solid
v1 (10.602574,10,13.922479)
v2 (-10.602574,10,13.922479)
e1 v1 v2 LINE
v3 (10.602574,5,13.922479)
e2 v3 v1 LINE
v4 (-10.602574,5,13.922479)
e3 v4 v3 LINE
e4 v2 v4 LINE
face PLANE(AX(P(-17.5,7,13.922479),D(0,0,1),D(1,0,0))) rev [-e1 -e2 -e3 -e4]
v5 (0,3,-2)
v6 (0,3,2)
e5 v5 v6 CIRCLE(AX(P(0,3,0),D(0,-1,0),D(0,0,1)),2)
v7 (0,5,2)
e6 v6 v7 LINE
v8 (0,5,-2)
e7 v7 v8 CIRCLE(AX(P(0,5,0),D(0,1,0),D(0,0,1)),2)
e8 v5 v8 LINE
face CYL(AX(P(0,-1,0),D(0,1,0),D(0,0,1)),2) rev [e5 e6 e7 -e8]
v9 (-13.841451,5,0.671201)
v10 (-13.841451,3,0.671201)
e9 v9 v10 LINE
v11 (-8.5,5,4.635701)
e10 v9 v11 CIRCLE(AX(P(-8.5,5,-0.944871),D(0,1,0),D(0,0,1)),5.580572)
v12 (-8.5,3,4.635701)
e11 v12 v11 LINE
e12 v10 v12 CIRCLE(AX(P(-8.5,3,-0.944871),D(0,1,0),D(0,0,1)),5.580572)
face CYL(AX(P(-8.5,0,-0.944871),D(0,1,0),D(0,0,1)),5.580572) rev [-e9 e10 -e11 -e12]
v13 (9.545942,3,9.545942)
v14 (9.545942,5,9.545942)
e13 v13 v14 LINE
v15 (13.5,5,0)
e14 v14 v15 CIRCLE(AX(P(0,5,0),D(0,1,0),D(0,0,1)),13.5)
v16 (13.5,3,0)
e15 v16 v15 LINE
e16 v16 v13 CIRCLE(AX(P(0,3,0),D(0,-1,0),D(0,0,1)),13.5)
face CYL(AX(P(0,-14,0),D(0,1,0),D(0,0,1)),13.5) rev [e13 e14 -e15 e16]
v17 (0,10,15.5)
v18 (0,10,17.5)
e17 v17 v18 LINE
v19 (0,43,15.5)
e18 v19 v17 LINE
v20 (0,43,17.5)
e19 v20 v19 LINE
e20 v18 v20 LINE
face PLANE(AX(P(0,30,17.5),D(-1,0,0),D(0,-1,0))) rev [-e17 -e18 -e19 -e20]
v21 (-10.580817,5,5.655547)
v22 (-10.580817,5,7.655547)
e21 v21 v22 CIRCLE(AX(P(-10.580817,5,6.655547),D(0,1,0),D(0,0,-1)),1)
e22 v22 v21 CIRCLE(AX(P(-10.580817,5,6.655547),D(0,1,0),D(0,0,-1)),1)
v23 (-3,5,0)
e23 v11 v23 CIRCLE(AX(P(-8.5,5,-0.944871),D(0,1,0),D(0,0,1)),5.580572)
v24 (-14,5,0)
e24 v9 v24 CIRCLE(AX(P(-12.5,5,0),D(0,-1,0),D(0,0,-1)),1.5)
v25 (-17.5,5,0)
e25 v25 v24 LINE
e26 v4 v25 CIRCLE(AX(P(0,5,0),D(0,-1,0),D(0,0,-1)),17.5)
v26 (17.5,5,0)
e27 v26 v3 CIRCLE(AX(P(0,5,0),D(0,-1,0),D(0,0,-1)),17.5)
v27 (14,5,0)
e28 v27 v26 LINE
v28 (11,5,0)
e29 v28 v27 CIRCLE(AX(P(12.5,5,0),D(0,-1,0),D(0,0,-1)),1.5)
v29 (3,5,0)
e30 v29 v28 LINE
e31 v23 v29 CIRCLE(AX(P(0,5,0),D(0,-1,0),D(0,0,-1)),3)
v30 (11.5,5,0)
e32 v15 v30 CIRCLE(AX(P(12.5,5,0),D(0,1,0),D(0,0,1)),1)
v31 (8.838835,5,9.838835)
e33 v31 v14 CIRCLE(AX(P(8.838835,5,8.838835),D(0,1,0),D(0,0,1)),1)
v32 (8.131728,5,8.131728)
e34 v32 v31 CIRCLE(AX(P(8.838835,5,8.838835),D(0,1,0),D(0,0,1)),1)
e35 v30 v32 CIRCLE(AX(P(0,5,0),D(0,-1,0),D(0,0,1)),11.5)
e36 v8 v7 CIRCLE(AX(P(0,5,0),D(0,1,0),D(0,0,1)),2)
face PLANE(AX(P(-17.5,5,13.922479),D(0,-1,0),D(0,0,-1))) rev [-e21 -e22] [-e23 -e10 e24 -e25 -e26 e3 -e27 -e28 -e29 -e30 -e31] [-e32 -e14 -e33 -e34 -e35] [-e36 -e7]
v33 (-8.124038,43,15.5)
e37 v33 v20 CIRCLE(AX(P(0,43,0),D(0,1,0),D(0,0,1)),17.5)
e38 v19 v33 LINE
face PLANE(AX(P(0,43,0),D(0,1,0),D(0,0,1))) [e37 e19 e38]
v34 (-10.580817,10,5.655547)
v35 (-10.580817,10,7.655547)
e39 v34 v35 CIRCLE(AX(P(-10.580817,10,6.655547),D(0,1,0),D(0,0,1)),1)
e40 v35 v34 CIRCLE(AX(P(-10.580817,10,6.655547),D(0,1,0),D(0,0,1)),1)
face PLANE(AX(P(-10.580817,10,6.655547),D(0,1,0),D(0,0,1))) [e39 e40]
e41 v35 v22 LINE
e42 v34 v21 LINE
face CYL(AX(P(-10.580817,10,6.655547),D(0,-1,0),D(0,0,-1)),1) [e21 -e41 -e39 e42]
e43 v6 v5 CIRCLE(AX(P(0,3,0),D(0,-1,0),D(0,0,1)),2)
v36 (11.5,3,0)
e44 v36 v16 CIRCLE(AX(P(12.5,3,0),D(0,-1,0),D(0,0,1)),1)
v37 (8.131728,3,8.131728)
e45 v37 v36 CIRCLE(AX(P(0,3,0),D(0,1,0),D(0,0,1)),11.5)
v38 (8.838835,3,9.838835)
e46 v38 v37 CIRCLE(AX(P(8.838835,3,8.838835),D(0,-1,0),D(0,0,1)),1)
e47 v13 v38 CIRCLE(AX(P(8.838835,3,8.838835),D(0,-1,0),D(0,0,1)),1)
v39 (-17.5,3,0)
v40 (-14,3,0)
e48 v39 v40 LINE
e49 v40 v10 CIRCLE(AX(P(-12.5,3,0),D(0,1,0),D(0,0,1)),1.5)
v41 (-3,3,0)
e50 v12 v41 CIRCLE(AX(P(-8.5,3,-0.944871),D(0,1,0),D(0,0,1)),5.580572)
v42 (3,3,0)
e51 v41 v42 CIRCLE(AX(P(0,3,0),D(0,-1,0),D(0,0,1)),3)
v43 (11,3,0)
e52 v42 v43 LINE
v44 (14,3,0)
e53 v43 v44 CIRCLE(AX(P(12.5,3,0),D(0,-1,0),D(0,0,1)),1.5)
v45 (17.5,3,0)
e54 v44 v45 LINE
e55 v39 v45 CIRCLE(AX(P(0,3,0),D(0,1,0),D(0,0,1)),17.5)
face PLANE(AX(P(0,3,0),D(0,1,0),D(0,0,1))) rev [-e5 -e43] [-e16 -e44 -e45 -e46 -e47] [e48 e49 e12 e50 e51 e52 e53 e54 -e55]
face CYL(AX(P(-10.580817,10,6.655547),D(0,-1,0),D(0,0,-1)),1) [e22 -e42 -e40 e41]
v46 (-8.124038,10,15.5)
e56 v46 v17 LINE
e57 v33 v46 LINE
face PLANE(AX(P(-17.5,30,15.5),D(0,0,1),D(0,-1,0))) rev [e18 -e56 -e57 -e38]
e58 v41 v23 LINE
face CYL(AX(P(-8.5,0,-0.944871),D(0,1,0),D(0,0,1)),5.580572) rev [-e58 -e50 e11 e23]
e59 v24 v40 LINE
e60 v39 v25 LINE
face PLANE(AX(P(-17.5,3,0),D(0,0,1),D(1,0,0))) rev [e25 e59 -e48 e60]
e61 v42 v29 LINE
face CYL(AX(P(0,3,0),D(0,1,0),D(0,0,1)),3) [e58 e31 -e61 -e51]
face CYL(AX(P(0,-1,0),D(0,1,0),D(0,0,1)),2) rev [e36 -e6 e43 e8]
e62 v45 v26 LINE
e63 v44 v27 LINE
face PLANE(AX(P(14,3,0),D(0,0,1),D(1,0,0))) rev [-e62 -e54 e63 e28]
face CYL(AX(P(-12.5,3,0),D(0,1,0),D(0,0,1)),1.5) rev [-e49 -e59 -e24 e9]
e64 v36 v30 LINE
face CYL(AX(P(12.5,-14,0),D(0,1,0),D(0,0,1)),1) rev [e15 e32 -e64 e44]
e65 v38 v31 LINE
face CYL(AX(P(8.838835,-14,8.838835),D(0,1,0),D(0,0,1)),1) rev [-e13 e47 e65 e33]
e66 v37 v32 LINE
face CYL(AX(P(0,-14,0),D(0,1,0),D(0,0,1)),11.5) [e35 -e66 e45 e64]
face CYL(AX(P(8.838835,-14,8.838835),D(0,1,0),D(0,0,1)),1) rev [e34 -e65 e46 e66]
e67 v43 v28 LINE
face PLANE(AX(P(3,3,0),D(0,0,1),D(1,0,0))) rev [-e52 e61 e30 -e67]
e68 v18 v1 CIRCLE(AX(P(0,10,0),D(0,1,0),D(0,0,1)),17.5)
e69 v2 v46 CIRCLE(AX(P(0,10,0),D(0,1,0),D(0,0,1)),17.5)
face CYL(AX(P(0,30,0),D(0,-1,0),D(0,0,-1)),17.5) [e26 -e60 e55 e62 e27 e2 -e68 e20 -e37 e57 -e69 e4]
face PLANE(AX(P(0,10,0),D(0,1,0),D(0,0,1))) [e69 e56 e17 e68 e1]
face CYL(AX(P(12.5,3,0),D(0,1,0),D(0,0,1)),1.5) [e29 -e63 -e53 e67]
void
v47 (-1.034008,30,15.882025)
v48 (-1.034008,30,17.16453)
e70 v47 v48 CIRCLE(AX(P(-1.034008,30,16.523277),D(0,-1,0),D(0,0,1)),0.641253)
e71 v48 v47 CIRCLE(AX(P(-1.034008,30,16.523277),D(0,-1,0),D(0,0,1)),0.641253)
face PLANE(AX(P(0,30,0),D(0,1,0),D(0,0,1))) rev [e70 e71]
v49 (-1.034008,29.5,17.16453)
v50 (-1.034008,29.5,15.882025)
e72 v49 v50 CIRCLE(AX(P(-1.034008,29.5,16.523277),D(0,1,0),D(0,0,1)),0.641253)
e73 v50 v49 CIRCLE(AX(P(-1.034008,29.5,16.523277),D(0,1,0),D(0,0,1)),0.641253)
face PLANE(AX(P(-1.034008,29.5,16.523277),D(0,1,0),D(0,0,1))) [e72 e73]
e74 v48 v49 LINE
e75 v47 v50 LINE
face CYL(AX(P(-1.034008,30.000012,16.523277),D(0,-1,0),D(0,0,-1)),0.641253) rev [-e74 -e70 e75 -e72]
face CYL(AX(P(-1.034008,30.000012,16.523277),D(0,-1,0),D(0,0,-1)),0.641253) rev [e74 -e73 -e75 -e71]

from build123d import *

# Parameters (mm, degrees)
SKETCH1_R                = 17.5
BOSS_EXTRUDE1_DEPTH      = 30
SKETCH2_R                = 4
BOSS_EXTRUDE2_DEPTH      = 2
CHAMFER1_SIZE            = 1
SKETCH4_R                = 2
BOSS_EXTRUDE3_DEPTH      = 12
SKETCH5_R                = 1.5
CUT_EXTRUDE1_DEPTH       = 12
CUT_EXTRUDE2_DEPTH       = 39.890872965
CUT_EXTRUDE2_DEPTH_BACK  = 39.890872965
SKETCH6_W                = 34.294260261
SKETCH6_H                = 28
CUT_EXTRUDE3_DEPTH       = 39.890872965
CUT_EXTRUDE3_DEPTH_BACK  = 39.890872965
SKETCH7_W                = 3
SKETCH7_H                = 23
CUT_EXTRUDE4_DEPTH       = 39.890872965
CUT_EXTRUDE4_DEPTH_BACK  = 39.890872965
SKETCH8_W                = 1.5
SKETCH8_H                = 5
CUT_EXTRUDE5_DEPTH       = 48.908767465
CUT_EXTRUDE5_DEPTH_BACK  = 48.908767465
SKETCH9_W                = 8.124038405
SKETCH9_H                = 23
CUT_EXTRUDE6_DEPTH       = 51.482670294
CUT_EXTRUDE6_DEPTH_BACK  = 0.5
SKETCH10_R               = 0.641252557
SKETCH11_R               = 17.5
BOSS_EXTRUDE4_DEPTH      = 5
CUT_EXTRUDE8_DEPTH       = 4
CUT_EXTRUDE9_DEPTH       = 39.890872965
CUT_EXTRUDE9_DEPTH_BACK  = 39.890872965
SKETCH13_W               = 19.268240878
SKETCH13_H               = 2
SKETCH14_R               = 2
CUT_EXTRUDE10_DEPTH      = 6
CUT_EXTRUDE11_DEPTH      = 39.890872965
CUT_EXTRUDE11_DEPTH_BACK = 39.890872965
SKETCH16_W               = 3.25
SKETCH16_H               = 3
CUT_EXTRUDE12_DEPTH      = 36.178118199
CUT_EXTRUDE13_START      = -17
SKETCH18_R               = 17.5
CUT_EXTRUDE13_DEPTH      = 17
BOSS_EXTRUDE5_DEPTH      = 3
BOSS_EXTRUDE6_DEPTH      = 13
CUT_EXTRUDE14_DEPTH      = 46.348649373
CUT_EXTRUDE14_DEPTH_BACK = 46.348649373
SKETCH21_R               = 1.5
SKETCH22_R               = 1
BOSS_EXTRUDE7_DEPTH      = 5
CUT_EXTRUDE15_DEPTH      = 5


with BuildPart() as part:
    # Sketch1 → Boss-Extrude1 (new body)
    with BuildSketch(Plane(origin=(0, 0, 0), x_dir=(1, 0, 0), z_dir=(0, 1, 0))):
        with Locations(Location((0, 0, 0), (0, 0, 270))):
            Circle(SKETCH1_R)
    extrude(amount=BOSS_EXTRUDE1_DEPTH)

    # Sketch2 → Boss-Extrude2 (add)
    with BuildSketch(Plane.XZ):
        with Locations(Location((0, 0, 0), (0, 0, 270))):
            Circle(SKETCH2_R)
    extrude(amount=BOSS_EXTRUDE2_DEPTH)

    # Chamfer1
    chamfer1_edges = [part.edges().sort_by_distance(p)[0] for p in [
        (0, 0, 4),
    ]]
    chamfer(chamfer1_edges, length=CHAMFER1_SIZE)

    # Sketch4 → Boss-Extrude3 (add)
    with BuildSketch(Plane.XZ.offset(2)):
        with Locations(Location((0, 0, 0), (0, 0, 270))):
            Circle(SKETCH4_R)
    extrude(amount=BOSS_EXTRUDE3_DEPTH)

    # Sketch5 → Cut-Extrude1 (cut)
    with BuildSketch(Plane.XZ.offset(14)):
        with Locations(Location((0, 0, 0), (0, 0, 270))):
            Circle(SKETCH5_R)
    extrude(amount=-CUT_EXTRUDE1_DEPTH, mode=Mode.SUBTRACT)

    # Sketch6 → Cut-Extrude2 (cut, two sides: drawn at the far end of the back side and taken through both)
    with BuildSketch(Plane(origin=(0, 0, 0), x_dir=(0, 0, -1), z_dir=(1, 0, 0)).offset(-CUT_EXTRUDE2_DEPTH_BACK)):
        with Locations((4.647130131, 16)):
            Rectangle(SKETCH6_W, SKETCH6_H)
    extrude(amount=CUT_EXTRUDE2_DEPTH + CUT_EXTRUDE2_DEPTH_BACK, mode=Mode.SUBTRACT)

    # Sketch7 → Cut-Extrude3 (cut, two sides: drawn at the far end of the back side and taken through both)
    with BuildSketch(Plane(origin=(0, 0, 0), x_dir=(0, 0, -1), z_dir=(1, 0, 0)).offset(-CUT_EXTRUDE3_DEPTH_BACK)):
        with Locations((-14, 18.5)):
            Rectangle(SKETCH7_W, SKETCH7_H)
    extrude(amount=CUT_EXTRUDE3_DEPTH + CUT_EXTRUDE3_DEPTH_BACK, mode=Mode.SUBTRACT)

    # Sketch8 → Cut-Extrude4 (cut, two sides: drawn at the far end of the back side and taken through both)
    with BuildSketch(Plane(origin=(0, 0, 0), x_dir=(0, 0, -1), z_dir=(1, 0, 0)).offset(-CUT_EXTRUDE4_DEPTH_BACK)):
        with Locations((-13.25, 4.5)):
            Rectangle(SKETCH8_W, SKETCH8_H)
    extrude(amount=CUT_EXTRUDE4_DEPTH + CUT_EXTRUDE4_DEPTH_BACK, mode=Mode.SUBTRACT)

    # Sketch9 → Cut-Extrude5 (cut, two sides: drawn at the far end of the back side and taken through both)
    with BuildSketch(Plane(origin=(0, 0, 15.5), x_dir=(-1, 0, 0), z_dir=(0, 0, -1)).offset(-CUT_EXTRUDE5_DEPTH_BACK)):
        with Locations((-4.062019203, 18.5)):
            Rectangle(SKETCH9_W, SKETCH9_H)
    extrude(amount=CUT_EXTRUDE5_DEPTH + CUT_EXTRUDE5_DEPTH_BACK, mode=Mode.SUBTRACT)

    # Sketch10 → Cut-Extrude6 (cut, two sides: drawn at the far end of the back side and taken through both)
    with BuildSketch(Plane(origin=(0, 30, 0), x_dir=(1, 0, 0), z_dir=(0, 1, 0)).offset(-CUT_EXTRUDE6_DEPTH_BACK)):
        with Locations(Location((-1.034007802, -16.523277445, 0), (0, 0, 270))):
            Circle(SKETCH10_R)
    extrude(amount=CUT_EXTRUDE6_DEPTH + CUT_EXTRUDE6_DEPTH_BACK, mode=Mode.SUBTRACT)

    # Sketch11 → Boss-Extrude4 (add)
    with BuildSketch(Plane(origin=(0, 2, 0), x_dir=(1, 0, 0), z_dir=(0, 1, 0))):
        with Locations(Location((0, 0, 0), (0, 0, 270))):
            Circle(SKETCH11_R)
    extrude(amount=BOSS_EXTRUDE4_DEPTH)

    # Sketch12 → Cut-Extrude8 (cut)
    with BuildSketch(Plane(origin=(0, 7, 0), x_dir=(1, 0, 0), z_dir=(0, 1, 0))):
        with BuildLine():
            Line((-17.5, 0), (-3, 0))
            ThreePointArc((-3, 0), (0, 3), (3, 0))
            Line((3, 0), (11, 0))
            ThreePointArc((11, 0), (12.5, 1.5), (14, 0))
            Line((14, 0), (18.571441089, 0))
            Line((18.571441089, 0), (18.571441089, 21.35501059))
            Line((18.571441089, 21.35501059), (-17.5, 21.35501059))
            Line((-17.5, 21.35501059), (-17.5, 0))
        make_face()
    extrude(amount=-CUT_EXTRUDE8_DEPTH, mode=Mode.SUBTRACT)

    # Sketch13 → Cut-Extrude9 (cut, two sides: drawn at the far end of the back side and taken through both)
    with BuildSketch(Plane(origin=(0, 0, 0), x_dir=(0, 0, -1), z_dir=(1, 0, 0)).offset(-CUT_EXTRUDE9_DEPTH_BACK)):
        with Locations((-4.288358488, 6)):
            Rectangle(SKETCH13_W, SKETCH13_H)
    extrude(amount=CUT_EXTRUDE9_DEPTH + CUT_EXTRUDE9_DEPTH_BACK, mode=Mode.SUBTRACT)

    # Sketch14 → Cut-Extrude10 (cut)
    with BuildSketch(Plane(origin=(0, 5, 0), x_dir=(1, 0, 0), z_dir=(0, 1, 0))):
        with Locations(Location((0, 0, 0), (0, 0, 90))):
            Circle(SKETCH14_R)
    extrude(amount=-CUT_EXTRUDE10_DEPTH, mode=Mode.SUBTRACT)

    # Sketch16 → Cut-Extrude11 (cut, two sides: drawn at the far end of the back side and taken through both)
    with BuildSketch(Plane(origin=(0, 0, 0), x_dir=(0, 0, -1), z_dir=(1, 0, 0)).offset(-CUT_EXTRUDE11_DEPTH_BACK)):
        with Locations((15.875, 1.5)):
            Rectangle(SKETCH16_W, SKETCH16_H)
    extrude(amount=CUT_EXTRUDE11_DEPTH + CUT_EXTRUDE11_DEPTH_BACK, mode=Mode.SUBTRACT)

    # Sketch17 → Cut-Extrude12 (cut, through all)
    with BuildSketch(Plane(origin=(0, 5, 0), x_dir=(1, 0, 0), z_dir=(0, 1, 0))):
        with BuildLine():
            ThreePointArc((9.545941546, -9.545941546), (12.472373689, -5.166226337), (13.5, 0))
            ThreePointArc((13.5, 0), (12.5, 1), (11.5, 0))
            ThreePointArc((11.5, 0), (10.624614624, -4.400859472), (8.131727984, -8.131727984))
            ThreePointArc((8.131727984, -8.131727984), (8.131727984, -9.545941546), (9.545941546, -9.545941546))
        make_face()
    extrude(amount=-CUT_EXTRUDE12_DEPTH, mode=Mode.SUBTRACT)

    # Sketch18 → Cut-Extrude13 (cut)
    with BuildSketch(Plane(origin=(0, 3, 0), x_dir=(1, 0, 0), z_dir=(0, 1, 0)).offset(CUT_EXTRUDE13_START)):
        Circle(SKETCH18_R)
    extrude(amount=CUT_EXTRUDE13_DEPTH, mode=Mode.SUBTRACT)

    # Sketch19 → Boss-Extrude5 (add)
    with BuildSketch(Plane(origin=(0, 7, 0), x_dir=(1, 0, 0), z_dir=(0, 1, 0))):
        with BuildLine():
            Line((10.602574241, -13.922478927), (-10.602574241, -13.922478927))
            ThreePointArc((-10.602574241, -13.922478927), (-9.396470001, -14.763344862), (-8.124038405, -15.5))
            Line((-8.124038405, -15.5), (0, -15.5))
            Line((0, -15.5), (0, -17.5))
            ThreePointArc((0, -17.5), (5.594936049, -16.581516535), (10.602574241, -13.922478927))
        make_face()
    extrude(amount=BOSS_EXTRUDE5_DEPTH)

    # Sketch20 → Boss-Extrude6 (add)
    with BuildSketch(Plane(origin=(0, 30, 0), x_dir=(1, 0, 0), z_dir=(0, 1, 0))):
        with BuildLine():
            Line((0, -17.5), (0, -15.5))
            Line((0, -15.5), (-8.124038405, -15.5))
            ThreePointArc((-8.124038405, -15.5), (-4.183300133, -16.992645468), (0, -17.5))
        make_face()
    extrude(amount=BOSS_EXTRUDE6_DEPTH)

    # Sketch21 → Cut-Extrude14 (cut, two sides: drawn at the far end of the back side and taken through both)
    with BuildSketch(Plane(origin=(0, 5, 0), x_dir=(1, 0, 0), z_dir=(0, 1, 0)).offset(-CUT_EXTRUDE14_DEPTH_BACK)):
        with Locations((-12.5, 0)):
            Circle(SKETCH21_R)
    extrude(amount=CUT_EXTRUDE14_DEPTH + CUT_EXTRUDE14_DEPTH_BACK, mode=Mode.SUBTRACT)

    # Sketch22 → Boss-Extrude7 (add)
    with BuildSketch(Plane(origin=(0, 5, 0), x_dir=(1, 0, 0), z_dir=(0, 1, 0))):
        with Locations(Location((-10.580817493, -6.655546647, 0), (0, 0, 90))):
            Circle(SKETCH22_R)
    extrude(amount=BOSS_EXTRUDE7_DEPTH)

    # Sketch23 → Cut-Extrude15 (cut)
    with BuildSketch(Plane(origin=(0, 5, 0), x_dir=(1, 0, 0), z_dir=(0, 1, 0))):
        with BuildLine():
            Line((-14, 0), (-3, 0))
            ThreePointArc((-3, 0), (-8.5, -4.635701065), (-14, 0))
        make_face()
    extrude(amount=-CUT_EXTRUDE15_DEPTH, mode=Mode.SUBTRACT)


solid = part.part
